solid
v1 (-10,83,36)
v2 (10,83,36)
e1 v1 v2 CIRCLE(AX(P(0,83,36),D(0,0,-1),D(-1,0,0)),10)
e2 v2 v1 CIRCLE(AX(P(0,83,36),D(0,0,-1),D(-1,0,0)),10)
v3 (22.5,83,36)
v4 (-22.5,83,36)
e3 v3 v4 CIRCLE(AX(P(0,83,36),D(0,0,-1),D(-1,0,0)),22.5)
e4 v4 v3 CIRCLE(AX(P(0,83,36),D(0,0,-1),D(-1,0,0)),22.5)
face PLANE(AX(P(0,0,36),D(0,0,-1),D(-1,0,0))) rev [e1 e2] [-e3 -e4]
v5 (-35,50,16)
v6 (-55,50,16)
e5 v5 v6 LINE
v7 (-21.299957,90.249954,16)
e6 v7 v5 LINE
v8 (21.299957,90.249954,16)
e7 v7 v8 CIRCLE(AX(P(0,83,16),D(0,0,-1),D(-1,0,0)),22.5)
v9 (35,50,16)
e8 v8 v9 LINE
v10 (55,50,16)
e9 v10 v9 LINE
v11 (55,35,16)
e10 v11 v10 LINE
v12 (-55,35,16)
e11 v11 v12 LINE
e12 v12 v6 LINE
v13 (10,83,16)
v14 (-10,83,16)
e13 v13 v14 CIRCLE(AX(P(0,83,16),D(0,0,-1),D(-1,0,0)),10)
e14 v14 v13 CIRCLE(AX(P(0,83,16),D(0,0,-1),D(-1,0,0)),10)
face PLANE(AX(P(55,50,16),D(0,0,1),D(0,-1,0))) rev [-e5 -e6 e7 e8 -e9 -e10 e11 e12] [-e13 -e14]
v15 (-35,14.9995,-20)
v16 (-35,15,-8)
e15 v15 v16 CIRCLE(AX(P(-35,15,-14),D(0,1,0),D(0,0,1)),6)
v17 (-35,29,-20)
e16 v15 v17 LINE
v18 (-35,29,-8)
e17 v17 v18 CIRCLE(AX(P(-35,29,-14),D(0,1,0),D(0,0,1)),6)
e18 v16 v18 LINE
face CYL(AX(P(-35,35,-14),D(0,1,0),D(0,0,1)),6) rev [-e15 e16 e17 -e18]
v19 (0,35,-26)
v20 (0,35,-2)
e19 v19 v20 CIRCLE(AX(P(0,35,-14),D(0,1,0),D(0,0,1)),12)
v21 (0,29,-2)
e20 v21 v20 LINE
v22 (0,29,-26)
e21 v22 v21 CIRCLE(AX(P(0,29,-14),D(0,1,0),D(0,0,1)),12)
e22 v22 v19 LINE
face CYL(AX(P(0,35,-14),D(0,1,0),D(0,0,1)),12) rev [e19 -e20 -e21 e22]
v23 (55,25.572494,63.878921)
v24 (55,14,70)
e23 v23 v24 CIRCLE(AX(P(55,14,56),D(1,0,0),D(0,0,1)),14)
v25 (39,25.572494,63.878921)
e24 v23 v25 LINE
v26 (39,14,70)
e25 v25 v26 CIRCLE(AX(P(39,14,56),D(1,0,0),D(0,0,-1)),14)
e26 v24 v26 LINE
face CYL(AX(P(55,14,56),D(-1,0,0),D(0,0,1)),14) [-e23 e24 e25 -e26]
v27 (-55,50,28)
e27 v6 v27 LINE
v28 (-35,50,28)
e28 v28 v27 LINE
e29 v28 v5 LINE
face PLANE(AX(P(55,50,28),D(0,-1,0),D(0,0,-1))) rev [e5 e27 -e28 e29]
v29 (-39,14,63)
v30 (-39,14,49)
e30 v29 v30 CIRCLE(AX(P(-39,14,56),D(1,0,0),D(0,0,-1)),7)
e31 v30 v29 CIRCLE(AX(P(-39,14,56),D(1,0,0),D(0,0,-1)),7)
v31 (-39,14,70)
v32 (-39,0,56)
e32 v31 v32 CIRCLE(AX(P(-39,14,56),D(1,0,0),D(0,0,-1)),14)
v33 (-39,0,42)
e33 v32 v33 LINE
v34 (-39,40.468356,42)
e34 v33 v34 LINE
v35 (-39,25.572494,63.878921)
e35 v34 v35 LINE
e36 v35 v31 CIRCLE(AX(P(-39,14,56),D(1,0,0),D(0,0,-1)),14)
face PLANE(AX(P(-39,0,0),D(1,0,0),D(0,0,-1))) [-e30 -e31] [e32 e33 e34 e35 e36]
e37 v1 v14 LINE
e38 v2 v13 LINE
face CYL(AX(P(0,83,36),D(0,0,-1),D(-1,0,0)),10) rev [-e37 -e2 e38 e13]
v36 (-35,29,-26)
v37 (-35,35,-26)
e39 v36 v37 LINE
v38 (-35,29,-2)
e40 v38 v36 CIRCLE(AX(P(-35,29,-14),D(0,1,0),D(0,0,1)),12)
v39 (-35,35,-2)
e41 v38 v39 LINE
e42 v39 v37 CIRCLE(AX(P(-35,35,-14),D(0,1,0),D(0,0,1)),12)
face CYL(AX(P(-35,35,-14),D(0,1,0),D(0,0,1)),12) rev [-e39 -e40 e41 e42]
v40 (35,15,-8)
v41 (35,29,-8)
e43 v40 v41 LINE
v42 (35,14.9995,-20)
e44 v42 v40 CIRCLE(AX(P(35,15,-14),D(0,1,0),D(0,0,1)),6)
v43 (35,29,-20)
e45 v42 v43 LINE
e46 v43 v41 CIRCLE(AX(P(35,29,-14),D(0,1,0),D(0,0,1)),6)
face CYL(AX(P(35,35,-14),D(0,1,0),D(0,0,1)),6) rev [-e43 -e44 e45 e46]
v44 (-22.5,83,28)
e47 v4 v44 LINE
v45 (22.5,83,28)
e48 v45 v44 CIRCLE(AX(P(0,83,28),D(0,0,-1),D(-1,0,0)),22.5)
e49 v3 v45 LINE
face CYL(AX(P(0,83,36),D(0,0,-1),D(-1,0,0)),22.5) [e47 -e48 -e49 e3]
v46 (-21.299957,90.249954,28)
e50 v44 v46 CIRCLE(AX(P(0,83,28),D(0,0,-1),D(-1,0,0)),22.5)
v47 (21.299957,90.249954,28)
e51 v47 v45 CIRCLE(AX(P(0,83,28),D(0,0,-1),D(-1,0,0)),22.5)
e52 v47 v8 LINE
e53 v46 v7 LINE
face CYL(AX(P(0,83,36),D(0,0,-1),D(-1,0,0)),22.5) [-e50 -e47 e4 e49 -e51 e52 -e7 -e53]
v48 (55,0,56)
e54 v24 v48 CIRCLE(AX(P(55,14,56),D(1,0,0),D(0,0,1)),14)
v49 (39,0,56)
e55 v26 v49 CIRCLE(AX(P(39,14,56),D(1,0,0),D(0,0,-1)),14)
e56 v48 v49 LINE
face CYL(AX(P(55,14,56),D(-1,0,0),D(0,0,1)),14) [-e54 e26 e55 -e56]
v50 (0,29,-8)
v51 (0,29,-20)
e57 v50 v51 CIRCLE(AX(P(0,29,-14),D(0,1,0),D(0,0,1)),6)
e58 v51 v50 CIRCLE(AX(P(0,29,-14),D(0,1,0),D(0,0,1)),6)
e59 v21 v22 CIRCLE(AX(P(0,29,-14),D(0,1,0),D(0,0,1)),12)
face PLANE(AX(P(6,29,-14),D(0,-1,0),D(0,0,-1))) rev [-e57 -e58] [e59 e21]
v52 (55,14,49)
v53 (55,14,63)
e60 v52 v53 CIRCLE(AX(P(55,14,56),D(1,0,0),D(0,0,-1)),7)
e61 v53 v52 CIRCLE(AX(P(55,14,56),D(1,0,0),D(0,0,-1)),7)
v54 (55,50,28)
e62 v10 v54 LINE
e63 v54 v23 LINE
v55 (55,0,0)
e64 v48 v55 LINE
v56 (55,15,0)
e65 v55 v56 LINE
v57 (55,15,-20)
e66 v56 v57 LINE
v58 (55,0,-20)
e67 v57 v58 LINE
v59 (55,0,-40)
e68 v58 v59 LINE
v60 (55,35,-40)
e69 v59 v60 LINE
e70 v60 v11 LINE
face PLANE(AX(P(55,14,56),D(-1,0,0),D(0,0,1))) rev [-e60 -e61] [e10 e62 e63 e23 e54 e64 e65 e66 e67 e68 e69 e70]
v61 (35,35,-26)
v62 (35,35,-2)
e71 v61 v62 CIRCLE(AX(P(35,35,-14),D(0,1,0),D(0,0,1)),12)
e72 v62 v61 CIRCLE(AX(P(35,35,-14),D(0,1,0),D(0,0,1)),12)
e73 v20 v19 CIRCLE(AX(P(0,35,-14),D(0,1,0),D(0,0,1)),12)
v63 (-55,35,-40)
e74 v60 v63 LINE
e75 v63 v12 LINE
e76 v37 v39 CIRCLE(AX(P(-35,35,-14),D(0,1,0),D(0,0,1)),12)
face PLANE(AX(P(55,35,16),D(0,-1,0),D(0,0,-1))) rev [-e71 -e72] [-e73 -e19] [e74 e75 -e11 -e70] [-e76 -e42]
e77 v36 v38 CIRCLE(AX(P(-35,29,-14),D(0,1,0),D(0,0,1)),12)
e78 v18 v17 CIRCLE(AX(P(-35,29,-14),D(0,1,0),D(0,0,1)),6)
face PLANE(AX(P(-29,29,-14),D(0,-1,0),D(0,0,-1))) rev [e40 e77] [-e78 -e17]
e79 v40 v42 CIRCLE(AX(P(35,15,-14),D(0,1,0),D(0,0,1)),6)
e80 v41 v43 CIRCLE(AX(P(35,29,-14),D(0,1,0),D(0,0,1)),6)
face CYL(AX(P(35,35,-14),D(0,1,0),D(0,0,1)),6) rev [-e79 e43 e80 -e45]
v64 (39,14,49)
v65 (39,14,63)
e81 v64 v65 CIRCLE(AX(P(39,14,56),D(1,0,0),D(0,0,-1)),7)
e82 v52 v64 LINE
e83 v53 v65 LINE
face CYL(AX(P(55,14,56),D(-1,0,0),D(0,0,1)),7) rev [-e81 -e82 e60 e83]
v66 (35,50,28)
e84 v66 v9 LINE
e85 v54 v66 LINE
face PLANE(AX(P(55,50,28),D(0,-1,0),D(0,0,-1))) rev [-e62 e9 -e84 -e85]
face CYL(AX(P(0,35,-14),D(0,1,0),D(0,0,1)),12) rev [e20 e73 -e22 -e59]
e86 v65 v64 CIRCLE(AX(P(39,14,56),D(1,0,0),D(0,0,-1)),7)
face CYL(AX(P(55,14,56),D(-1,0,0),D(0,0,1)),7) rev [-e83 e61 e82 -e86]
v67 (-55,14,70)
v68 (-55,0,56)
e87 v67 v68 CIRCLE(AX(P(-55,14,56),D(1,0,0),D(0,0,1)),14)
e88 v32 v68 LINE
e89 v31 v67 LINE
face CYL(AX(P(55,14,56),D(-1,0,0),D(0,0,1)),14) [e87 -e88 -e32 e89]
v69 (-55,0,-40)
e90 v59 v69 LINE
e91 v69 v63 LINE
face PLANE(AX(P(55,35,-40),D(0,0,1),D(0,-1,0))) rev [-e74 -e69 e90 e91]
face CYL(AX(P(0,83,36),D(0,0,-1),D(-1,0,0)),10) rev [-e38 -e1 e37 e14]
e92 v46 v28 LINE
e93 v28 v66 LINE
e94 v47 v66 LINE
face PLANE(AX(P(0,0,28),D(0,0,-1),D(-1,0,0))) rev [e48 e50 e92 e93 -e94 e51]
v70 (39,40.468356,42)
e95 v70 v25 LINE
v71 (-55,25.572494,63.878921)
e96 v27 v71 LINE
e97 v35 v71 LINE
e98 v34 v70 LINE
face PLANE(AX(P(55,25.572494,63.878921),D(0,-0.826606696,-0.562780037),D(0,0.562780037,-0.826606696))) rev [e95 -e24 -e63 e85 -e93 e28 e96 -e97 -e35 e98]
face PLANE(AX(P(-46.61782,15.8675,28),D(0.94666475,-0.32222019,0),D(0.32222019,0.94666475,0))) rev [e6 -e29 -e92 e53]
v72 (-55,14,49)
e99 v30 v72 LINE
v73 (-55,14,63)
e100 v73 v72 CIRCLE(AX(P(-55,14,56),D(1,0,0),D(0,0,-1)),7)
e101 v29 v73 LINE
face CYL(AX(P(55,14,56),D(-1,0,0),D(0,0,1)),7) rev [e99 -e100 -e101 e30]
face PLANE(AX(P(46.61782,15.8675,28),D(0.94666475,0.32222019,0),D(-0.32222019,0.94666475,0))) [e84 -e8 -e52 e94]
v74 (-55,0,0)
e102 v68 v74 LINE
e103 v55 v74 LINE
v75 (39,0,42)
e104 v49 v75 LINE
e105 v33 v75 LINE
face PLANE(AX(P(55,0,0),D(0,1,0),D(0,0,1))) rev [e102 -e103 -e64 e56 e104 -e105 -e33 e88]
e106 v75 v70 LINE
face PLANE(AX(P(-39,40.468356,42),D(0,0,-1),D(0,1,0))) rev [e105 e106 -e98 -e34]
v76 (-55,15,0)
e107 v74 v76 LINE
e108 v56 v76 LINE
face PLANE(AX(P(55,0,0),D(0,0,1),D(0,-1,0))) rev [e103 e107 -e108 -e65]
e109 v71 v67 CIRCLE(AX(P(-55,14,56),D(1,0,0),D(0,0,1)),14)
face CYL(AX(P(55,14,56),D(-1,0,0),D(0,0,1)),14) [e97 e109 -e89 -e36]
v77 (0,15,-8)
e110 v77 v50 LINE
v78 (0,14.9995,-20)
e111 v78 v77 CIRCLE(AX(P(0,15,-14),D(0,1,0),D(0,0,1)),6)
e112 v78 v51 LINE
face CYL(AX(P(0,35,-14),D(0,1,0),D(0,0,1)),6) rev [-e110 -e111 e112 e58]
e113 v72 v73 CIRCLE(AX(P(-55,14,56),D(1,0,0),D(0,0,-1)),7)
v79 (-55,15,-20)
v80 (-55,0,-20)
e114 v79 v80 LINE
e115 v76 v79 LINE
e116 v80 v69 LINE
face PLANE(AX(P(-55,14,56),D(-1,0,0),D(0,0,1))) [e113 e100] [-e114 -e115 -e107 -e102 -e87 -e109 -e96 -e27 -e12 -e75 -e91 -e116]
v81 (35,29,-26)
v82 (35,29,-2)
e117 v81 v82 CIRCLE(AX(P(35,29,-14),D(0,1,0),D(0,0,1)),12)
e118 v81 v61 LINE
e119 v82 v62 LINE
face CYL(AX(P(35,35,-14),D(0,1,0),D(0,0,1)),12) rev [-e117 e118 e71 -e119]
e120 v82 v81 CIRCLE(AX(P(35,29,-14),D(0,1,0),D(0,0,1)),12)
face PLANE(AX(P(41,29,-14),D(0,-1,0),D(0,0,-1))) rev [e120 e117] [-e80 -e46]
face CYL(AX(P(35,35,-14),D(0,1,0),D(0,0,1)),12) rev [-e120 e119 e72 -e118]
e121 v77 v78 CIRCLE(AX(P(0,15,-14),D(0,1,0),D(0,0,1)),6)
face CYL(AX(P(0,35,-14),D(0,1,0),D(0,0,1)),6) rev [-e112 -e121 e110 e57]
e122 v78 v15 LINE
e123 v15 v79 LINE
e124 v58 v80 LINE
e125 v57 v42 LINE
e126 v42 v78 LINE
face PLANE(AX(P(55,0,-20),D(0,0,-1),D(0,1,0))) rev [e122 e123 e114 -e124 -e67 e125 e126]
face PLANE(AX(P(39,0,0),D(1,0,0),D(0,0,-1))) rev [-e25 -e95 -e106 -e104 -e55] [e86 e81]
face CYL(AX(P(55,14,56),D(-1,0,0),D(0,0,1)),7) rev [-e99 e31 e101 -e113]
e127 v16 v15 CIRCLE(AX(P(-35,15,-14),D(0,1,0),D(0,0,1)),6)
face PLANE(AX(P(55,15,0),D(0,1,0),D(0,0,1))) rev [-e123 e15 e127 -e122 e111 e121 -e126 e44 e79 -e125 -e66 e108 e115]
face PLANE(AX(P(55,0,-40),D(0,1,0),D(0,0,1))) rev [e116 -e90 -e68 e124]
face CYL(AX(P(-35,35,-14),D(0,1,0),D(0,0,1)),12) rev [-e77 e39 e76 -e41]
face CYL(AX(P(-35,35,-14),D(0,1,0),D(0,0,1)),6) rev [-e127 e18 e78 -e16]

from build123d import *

# Parameters (mm, degrees)
BASE_PROFILE_SKETCH_R             = 7
BASE_BODY_DEPTH                   = 55
RECESS_PROFILE_SKETCH_W           = 28
RECESS_PROFILE_SKETCH_H           = 40.468356276
RECESS_CUT_78_DEPTH               = 39
EYELET_LUG_SKETCH_R               = 22.5
EYELET_LUG_SKETCH_R_2             = 10
EYELET_LUG_20_DEPTH               = 20
EYELET_WEB_12_DEPTH               = 12
COUNTERBORED_HOLES_12_D           = 12
COUNTERBORED_HOLES_12_CBORE_D     = 24
COUNTERBORED_HOLES_12_CBORE_DEPTH = 6


with BuildPart() as part:
    # Base Profile Sketch → Base Body (new, symmetric)
    with BuildSketch(Plane(origin=(0, 0, 0), x_dir=(0, 0, -1), z_dir=(1, 0, 0))):
        with BuildLine():
            Line((40, 0), (20, 0))
            Line((20, 0), (20, 15))
            Line((20, 15), (0, 15))
            Line((0, 15), (0, 0))
            Line((0, 0), (-56, 0))
            ThreePointArc((-56, 0), (-69.379366808, 9.877798669), (-63.878920524, 25.572493741))
            Line((-63.878920524, 25.572493741), (-28, 50))
            Line((-28, 50), (-16, 50))
            Line((-16, 50), (-16, 35))
            Line((-16, 35), (40, 35))
            Line((40, 35), (40, 0))
        make_face()
        with Locations((-56, 14)):
            Circle(BASE_PROFILE_SKETCH_R, mode=Mode.SUBTRACT)
    extrude(amount=BASE_BODY_DEPTH, both=True)

    # Recess Profile Sketch → Recess Cut 78 (cut, symmetric)
    with BuildSketch(Plane(origin=(0, 0, 0), x_dir=(0, 0, -1), z_dir=(1, 0, 0))):
        with Locations((-56, 20.234178138)):
            Rectangle(RECESS_PROFILE_SKETCH_W, RECESS_PROFILE_SKETCH_H)
    extrude(amount=RECESS_CUT_78_DEPTH, both=True, mode=Mode.SUBTRACT)



with BuildPart() as body_2:
    # Eyelet Lug Sketch → Eyelet Lug 20 (new body)
    with BuildSketch(Plane(origin=(0, 0, 16), x_dir=(-1, 0, 0), z_dir=(0, 0, -1))):
        with Locations((0, 83)):
            Circle(EYELET_LUG_SKETCH_R)
        with Locations((0, 83)):
            Circle(EYELET_LUG_SKETCH_R_2, mode=Mode.SUBTRACT)
    extrude(amount=-EYELET_LUG_20_DEPTH)


with BuildPart() as part_1:
    add(part.part)

    add(body_2.part)  # Eyelet Web 12 merges body 2
    # Sketch4_3 → Eyelet Web 12 (add)
    with BuildSketch(Plane(origin=(0, 0, 16), x_dir=(-1, 0, 0), z_dir=(0, 0, -1))):
        with BuildLine():
            Line((-35, 50), (0, 50))
            Line((0, 50), (0, 60.5))
            ThreePointArc((0, 60.5), (-18.294452315, 69.901793463), (-21.299956881, 90.249954267))
            Line((-21.299956881, 90.249954267), (-35, 50))
        make_face()
        with BuildLine():
            Line((0, 60.5), (0, 50))
            Line((0, 50), (35, 50))
            Line((35, 50), (21.299956881, 90.249954267))
            ThreePointArc((21.299956881, 90.249954267), (22.197961954, 86.674300626), (22.5, 83))
            ThreePointArc((22.5, 83), (15.909902577, 67.090097423), (0, 60.5))
        make_face()
    extrude(amount=-EYELET_WEB_12_DEPTH)

    # Counterbored Holes _12 (through all)
    with Locations(Plane(origin=(0, 35, 0), x_dir=(1, 0, 0), z_dir=(0, 1, 0))):
        with Locations((35, 14), (0, 14), (-35, 14)):
            CounterBoreHole(COUNTERBORED_HOLES_12_D / 2, COUNTERBORED_HOLES_12_CBORE_D / 2, COUNTERBORED_HOLES_12_CBORE_DEPTH)


solid = part_1.part
